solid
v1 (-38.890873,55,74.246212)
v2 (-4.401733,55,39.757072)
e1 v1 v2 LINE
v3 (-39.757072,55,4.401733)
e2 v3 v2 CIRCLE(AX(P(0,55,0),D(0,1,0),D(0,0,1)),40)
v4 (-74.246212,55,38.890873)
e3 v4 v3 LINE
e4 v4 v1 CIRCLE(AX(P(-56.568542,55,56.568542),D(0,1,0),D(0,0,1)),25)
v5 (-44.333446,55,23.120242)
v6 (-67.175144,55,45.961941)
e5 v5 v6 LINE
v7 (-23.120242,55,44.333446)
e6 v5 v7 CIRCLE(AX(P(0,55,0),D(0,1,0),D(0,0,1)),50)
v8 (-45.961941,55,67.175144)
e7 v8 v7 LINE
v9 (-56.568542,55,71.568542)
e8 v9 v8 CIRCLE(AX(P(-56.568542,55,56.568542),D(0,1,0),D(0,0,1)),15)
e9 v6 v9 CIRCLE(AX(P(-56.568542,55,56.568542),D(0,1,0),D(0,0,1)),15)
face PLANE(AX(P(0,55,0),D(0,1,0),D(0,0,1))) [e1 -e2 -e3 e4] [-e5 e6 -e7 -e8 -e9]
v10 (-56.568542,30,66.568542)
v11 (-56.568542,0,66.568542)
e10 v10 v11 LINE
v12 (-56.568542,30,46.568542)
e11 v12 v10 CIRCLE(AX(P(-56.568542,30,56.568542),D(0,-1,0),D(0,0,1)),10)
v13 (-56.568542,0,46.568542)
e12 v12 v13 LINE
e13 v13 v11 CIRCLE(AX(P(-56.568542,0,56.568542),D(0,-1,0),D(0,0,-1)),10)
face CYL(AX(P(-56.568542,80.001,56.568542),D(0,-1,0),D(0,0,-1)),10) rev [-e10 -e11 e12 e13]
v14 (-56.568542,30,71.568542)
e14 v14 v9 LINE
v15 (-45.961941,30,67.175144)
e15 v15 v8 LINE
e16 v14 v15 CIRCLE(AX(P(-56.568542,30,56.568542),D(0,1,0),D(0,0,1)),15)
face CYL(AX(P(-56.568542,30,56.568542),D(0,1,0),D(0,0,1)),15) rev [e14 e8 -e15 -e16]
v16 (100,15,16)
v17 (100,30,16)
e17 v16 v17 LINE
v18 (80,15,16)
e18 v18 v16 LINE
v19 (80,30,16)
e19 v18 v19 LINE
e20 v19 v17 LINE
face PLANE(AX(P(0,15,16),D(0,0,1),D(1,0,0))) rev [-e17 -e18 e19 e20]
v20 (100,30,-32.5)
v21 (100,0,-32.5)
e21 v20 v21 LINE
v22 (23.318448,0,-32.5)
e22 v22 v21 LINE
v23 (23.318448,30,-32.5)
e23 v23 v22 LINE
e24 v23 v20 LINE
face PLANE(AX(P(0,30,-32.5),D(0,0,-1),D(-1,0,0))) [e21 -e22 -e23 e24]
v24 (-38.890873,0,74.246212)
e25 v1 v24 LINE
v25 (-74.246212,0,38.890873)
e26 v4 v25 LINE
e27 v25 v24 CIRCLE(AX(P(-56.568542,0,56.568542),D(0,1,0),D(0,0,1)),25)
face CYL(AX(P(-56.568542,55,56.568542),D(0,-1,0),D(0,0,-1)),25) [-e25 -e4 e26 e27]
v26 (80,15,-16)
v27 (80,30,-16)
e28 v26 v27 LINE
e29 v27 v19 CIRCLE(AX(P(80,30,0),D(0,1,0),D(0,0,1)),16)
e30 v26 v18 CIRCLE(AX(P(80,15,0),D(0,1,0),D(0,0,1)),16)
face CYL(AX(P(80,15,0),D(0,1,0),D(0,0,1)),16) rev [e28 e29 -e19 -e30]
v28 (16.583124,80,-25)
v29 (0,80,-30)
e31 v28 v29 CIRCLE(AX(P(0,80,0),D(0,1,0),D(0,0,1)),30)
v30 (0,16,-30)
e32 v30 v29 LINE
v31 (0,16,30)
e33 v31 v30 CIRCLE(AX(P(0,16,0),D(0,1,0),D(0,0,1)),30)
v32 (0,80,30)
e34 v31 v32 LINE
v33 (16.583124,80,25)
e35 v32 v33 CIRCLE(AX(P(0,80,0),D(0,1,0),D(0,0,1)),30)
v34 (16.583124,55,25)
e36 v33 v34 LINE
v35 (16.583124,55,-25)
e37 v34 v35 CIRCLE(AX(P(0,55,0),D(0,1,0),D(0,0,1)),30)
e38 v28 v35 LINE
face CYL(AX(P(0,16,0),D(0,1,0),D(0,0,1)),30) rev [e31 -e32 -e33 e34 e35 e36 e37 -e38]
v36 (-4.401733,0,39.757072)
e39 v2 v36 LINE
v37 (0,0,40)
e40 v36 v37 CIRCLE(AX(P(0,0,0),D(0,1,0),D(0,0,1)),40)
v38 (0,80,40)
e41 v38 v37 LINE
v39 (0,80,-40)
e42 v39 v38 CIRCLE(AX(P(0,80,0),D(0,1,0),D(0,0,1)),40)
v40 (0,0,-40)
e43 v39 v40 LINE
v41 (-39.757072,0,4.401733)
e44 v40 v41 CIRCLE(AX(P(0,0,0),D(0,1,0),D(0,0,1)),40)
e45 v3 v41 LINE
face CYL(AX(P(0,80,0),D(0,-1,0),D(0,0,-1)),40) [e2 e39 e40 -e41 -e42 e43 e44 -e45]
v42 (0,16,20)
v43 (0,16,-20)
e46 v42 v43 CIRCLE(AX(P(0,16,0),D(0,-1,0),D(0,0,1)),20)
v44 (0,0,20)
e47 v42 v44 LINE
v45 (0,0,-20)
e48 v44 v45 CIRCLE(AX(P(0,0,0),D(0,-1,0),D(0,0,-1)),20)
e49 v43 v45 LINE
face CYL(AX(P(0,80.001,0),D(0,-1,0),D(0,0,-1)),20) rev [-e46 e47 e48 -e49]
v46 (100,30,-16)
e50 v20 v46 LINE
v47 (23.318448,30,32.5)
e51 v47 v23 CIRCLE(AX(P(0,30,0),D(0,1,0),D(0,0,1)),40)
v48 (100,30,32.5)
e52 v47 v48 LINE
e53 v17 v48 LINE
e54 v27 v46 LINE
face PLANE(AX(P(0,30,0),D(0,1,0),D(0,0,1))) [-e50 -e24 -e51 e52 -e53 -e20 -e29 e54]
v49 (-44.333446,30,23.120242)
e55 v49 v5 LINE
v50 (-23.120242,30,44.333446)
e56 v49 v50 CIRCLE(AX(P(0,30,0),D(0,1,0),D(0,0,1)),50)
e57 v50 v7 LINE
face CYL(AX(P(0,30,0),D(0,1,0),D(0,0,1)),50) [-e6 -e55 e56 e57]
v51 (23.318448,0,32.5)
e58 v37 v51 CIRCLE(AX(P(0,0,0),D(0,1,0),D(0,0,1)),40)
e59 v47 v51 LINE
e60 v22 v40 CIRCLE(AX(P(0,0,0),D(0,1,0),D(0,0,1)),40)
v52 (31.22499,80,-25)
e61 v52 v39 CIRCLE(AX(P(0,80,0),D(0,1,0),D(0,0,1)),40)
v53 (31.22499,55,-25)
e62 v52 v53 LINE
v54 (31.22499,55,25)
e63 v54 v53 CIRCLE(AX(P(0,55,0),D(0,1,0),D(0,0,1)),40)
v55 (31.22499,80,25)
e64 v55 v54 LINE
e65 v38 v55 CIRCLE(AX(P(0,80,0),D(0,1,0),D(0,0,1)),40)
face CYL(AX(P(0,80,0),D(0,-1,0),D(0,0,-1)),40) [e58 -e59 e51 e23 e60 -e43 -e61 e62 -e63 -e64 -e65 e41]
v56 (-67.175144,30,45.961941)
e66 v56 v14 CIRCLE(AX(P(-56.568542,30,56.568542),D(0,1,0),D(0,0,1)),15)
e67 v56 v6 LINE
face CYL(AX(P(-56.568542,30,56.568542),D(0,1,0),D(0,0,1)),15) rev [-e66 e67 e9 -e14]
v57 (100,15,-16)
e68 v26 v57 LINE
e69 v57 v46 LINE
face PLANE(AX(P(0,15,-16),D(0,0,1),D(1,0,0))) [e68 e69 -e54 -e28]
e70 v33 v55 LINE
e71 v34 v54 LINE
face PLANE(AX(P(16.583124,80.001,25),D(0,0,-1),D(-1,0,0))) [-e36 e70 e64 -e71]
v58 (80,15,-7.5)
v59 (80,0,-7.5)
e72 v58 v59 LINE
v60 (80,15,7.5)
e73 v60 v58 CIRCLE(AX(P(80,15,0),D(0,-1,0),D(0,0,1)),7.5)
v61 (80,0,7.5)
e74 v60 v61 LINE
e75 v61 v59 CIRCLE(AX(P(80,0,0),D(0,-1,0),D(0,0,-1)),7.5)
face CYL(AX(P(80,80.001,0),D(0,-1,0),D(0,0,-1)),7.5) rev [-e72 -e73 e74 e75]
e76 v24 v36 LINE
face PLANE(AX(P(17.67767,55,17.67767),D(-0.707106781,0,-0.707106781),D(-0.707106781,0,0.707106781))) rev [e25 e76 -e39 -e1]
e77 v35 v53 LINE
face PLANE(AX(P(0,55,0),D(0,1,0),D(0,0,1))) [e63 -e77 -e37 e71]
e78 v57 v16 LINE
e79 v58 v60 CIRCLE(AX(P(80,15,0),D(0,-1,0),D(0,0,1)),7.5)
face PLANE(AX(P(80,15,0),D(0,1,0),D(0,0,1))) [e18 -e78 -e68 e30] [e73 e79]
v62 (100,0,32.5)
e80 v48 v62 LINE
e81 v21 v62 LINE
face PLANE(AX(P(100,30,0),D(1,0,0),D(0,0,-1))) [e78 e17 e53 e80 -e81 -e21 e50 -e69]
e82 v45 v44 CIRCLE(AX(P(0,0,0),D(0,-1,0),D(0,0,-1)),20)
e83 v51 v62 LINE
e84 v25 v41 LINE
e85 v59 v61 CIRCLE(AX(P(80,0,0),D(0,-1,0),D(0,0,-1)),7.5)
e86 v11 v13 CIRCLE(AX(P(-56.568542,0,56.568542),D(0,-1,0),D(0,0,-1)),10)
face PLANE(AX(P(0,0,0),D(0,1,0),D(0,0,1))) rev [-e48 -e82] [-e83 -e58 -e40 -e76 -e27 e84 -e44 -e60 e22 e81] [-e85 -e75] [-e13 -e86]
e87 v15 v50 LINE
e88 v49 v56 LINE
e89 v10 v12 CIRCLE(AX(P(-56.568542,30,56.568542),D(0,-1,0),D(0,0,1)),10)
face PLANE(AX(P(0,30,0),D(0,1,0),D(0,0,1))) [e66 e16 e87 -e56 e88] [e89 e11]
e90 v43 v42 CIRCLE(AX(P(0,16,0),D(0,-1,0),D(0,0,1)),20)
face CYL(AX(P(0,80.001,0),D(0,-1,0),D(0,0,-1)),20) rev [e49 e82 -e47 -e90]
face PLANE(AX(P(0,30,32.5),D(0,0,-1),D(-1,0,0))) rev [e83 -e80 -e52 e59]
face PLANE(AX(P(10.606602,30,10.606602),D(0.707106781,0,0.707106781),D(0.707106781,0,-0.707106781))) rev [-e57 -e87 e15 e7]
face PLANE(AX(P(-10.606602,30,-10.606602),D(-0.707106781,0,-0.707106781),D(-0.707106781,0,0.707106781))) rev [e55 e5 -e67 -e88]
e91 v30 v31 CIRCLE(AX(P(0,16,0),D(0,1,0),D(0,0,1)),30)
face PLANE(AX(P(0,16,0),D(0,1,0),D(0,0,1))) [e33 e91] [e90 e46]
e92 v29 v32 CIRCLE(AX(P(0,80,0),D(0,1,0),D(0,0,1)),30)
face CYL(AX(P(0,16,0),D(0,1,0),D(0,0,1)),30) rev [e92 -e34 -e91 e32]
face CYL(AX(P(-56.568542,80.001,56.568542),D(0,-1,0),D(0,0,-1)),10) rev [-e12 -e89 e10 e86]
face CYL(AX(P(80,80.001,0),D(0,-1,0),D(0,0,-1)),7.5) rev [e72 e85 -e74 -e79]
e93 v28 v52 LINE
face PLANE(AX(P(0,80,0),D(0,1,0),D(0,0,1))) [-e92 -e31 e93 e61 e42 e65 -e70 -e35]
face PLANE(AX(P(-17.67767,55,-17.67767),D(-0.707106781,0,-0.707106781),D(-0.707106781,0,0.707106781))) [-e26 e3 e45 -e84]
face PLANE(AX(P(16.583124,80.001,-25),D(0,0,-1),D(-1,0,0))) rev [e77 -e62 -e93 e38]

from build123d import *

# Parameters (mm, degrees)
HUB_PROFILE_SKETCH_R       = 40
HUB_CYLINDER_80_DEPTH      = 80
SIDE_TAB_DEPTH             = 55
ANGLED_ARM_45DEG_DEPTH     = 30
ARM_SLOT_POCKET_DEPTH      = 25
TAB_START                  = -25
TAB_SLOT_COUNTERBORE_DEPTH = 15
TAB_THROUGH_HOLE_REACH     = 142.28
HUB_START                  = 16
SKETCH1_3_R                = 30
HUB_BORE_60_DEPTH          = 64
HUB_WALL_NOTCH_REACH       = 153.834
HUB_NOTCH_SKETCH_R         = 10
HUB_NOTCH_SKETCH_R_2       = 7.5
HUB_NOTCH_SKETCH_R_3       = 20


with BuildPart() as part:
    # Hub Profile Sketch → Hub Cylinder _80 (new body)
    with BuildSketch(Plane(origin=(0, 0, 0), x_dir=(1, 0, 0), z_dir=(0, 1, 0))):
        with Locations(Location((0, 0, 0), (0, 0, 270))):
            Circle(HUB_PROFILE_SKETCH_R)
    extrude(amount=HUB_CYLINDER_80_DEPTH)

    # Arm and Tab Sketch → Side Tab (add)
    with BuildSketch(Plane(origin=(0, 0, 0), x_dir=(1, 0, 0), z_dir=(0, 1, 0))):
        with BuildLine():
            ThreePointArc((-39.757071695, -4.401732636), (-28.284271247, -28.284271247), (-4.401732636, -39.757071695))
            Line((-4.401732636, -39.757071695), (-38.890872965, -74.246212025))
            ThreePointArc((-38.890872965, -74.246212025), (-74.246212025, -74.246212025), (-74.246212025, -38.890872965))
            Line((-74.246212025, -38.890872965), (-39.757071695, -4.401732636))
        make_face()
    extrude(amount=SIDE_TAB_DEPTH)

    # Sketch3_3 → Angled Arm 45deg (add)
    with BuildSketch(Plane(origin=(0, 0, 0), x_dir=(1, 0, 0), z_dir=(0, 1, 0))):
        with BuildLine():
            ThreePointArc((23.318447633, -32.5), (40, 0), (23.318447633, 32.5))
            Line((23.318447633, 32.5), (100, 32.5))
            Line((100, 32.5), (100, -32.5))
            Line((100, -32.5), (23.318447633, -32.5))
        make_face()
    extrude(amount=ANGLED_ARM_45DEG_DEPTH)

    # Slot and Hole Sketch → Arm Slot Pocket (cut)
    with BuildSketch(Plane(origin=(0, 55, 0), x_dir=(1, 0, 0), z_dir=(0, 1, 0))):
        with BuildLine():
            Line((-44.333445626, -23.12024219), (-67.175144213, -45.961940777))
            ThreePointArc((-67.175144213, -45.961940777), (-67.175144213, -67.175144213), (-45.961940777, -67.175144213))
            Line((-45.961940777, -67.175144213), (-23.12024219, -44.333445626))
            ThreePointArc((-23.12024219, -44.333445626), (-35.355339059, -35.355339059), (-44.333445626, -23.12024219))
        make_face()
    extrude(amount=-ARM_SLOT_POCKET_DEPTH, mode=Mode.SUBTRACT)

    # Sketch4_3 → Tab Slot Counterbore (cut)
    with BuildSketch(Plane(origin=(0, 55, 0), x_dir=(1, 0, 0), z_dir=(0, 1, 0)).offset(TAB_START)):
        with BuildLine():
            Line((100, 16), (100, -16))
            Line((100, -16), (80, -16))
            ThreePointArc((80, -16), (64, 0), (80, 16))
            Line((80, 16), (100, 16))
        make_face()
    extrude(amount=-TAB_SLOT_COUNTERBORE_DEPTH, mode=Mode.SUBTRACT)

    # Sketch4_4 → Tab Through Hole (cut, up to next)
    with BuildSketch(Plane(origin=(0, 55, 0), x_dir=(1, 0, 0), z_dir=(0, 1, 0)), mode=Mode.PRIVATE) as tab_through_hole_sk1:
        with BuildLine():
            Line((16.583123952, 25), (31.224989992, 25))
            ThreePointArc((31.224989992, 25), (40, 0), (31.224989992, -25))
            Line((31.224989992, -25), (16.583123952, -25))
            ThreePointArc((16.583123952, -25), (30, 0), (16.583123952, 25))
        make_face()
    tab_through_hole_tool1 = extrude(tab_through_hole_sk1.sketch, amount=TAB_THROUGH_HOLE_REACH, mode=Mode.PRIVATE) & part.part
    add(tab_through_hole_tool1.solids().sort_by_distance((31.26913, 55, 0))[0], mode=Mode.SUBTRACT)

    # Sketch1_3 → Hub Bore _60 (cut)
    with BuildSketch(Plane(origin=(0, 0, 0), x_dir=(1, 0, 0), z_dir=(0, 1, 0)).offset(HUB_START)):
        with Locations(Location((0, 0, 0), (0, 0, 270))):
            Circle(SKETCH1_3_R)
    extrude(amount=HUB_BORE_60_DEPTH, mode=Mode.SUBTRACT)

    # Hub Notch Sketch → Hub Wall Notch (cut, up to next)
    with BuildSketch(Plane.XZ, mode=Mode.PRIVATE) as hub_wall_notch_sk1:
        with Locations(Location((-56.568542495, 56.568542495, 0), (0, 0, 270))):
            Circle(HUB_NOTCH_SKETCH_R)
    hub_wall_notch_tool1 = extrude(hub_wall_notch_sk1.sketch, amount=-HUB_WALL_NOTCH_REACH, mode=Mode.PRIVATE) & part.part
    # Hub Notch Sketch → Hub Wall Notch (cut, up to next)
    with BuildSketch(Plane.XZ, mode=Mode.PRIVATE) as hub_wall_notch_sk2:
        with Locations(Location((80, 0, 0), (0, 0, 270))):
            Circle(HUB_NOTCH_SKETCH_R_2)
    hub_wall_notch_tool2 = extrude(hub_wall_notch_sk2.sketch, amount=-HUB_WALL_NOTCH_REACH, mode=Mode.PRIVATE) & part.part
    # Hub Notch Sketch → Hub Wall Notch (cut, up to next)
    with BuildSketch(Plane.XZ, mode=Mode.PRIVATE) as hub_wall_notch_sk3:
        with Locations(Location((0, 0, 0), (0, 0, 270))):
            Circle(HUB_NOTCH_SKETCH_R_3)
    hub_wall_notch_tool3 = extrude(hub_wall_notch_sk3.sketch, amount=-HUB_WALL_NOTCH_REACH, mode=Mode.PRIVATE) & part.part
    add(hub_wall_notch_tool1.solids().sort_by_distance((-56.568542, 0, 56.568542))[0], mode=Mode.SUBTRACT)
    add(hub_wall_notch_tool2.solids().sort_by_distance((80, 0, 0))[0], mode=Mode.SUBTRACT)
    add(hub_wall_notch_tool3.solids().sort_by_distance((0, 0, 0))[0], mode=Mode.SUBTRACT)


solid = part.part
